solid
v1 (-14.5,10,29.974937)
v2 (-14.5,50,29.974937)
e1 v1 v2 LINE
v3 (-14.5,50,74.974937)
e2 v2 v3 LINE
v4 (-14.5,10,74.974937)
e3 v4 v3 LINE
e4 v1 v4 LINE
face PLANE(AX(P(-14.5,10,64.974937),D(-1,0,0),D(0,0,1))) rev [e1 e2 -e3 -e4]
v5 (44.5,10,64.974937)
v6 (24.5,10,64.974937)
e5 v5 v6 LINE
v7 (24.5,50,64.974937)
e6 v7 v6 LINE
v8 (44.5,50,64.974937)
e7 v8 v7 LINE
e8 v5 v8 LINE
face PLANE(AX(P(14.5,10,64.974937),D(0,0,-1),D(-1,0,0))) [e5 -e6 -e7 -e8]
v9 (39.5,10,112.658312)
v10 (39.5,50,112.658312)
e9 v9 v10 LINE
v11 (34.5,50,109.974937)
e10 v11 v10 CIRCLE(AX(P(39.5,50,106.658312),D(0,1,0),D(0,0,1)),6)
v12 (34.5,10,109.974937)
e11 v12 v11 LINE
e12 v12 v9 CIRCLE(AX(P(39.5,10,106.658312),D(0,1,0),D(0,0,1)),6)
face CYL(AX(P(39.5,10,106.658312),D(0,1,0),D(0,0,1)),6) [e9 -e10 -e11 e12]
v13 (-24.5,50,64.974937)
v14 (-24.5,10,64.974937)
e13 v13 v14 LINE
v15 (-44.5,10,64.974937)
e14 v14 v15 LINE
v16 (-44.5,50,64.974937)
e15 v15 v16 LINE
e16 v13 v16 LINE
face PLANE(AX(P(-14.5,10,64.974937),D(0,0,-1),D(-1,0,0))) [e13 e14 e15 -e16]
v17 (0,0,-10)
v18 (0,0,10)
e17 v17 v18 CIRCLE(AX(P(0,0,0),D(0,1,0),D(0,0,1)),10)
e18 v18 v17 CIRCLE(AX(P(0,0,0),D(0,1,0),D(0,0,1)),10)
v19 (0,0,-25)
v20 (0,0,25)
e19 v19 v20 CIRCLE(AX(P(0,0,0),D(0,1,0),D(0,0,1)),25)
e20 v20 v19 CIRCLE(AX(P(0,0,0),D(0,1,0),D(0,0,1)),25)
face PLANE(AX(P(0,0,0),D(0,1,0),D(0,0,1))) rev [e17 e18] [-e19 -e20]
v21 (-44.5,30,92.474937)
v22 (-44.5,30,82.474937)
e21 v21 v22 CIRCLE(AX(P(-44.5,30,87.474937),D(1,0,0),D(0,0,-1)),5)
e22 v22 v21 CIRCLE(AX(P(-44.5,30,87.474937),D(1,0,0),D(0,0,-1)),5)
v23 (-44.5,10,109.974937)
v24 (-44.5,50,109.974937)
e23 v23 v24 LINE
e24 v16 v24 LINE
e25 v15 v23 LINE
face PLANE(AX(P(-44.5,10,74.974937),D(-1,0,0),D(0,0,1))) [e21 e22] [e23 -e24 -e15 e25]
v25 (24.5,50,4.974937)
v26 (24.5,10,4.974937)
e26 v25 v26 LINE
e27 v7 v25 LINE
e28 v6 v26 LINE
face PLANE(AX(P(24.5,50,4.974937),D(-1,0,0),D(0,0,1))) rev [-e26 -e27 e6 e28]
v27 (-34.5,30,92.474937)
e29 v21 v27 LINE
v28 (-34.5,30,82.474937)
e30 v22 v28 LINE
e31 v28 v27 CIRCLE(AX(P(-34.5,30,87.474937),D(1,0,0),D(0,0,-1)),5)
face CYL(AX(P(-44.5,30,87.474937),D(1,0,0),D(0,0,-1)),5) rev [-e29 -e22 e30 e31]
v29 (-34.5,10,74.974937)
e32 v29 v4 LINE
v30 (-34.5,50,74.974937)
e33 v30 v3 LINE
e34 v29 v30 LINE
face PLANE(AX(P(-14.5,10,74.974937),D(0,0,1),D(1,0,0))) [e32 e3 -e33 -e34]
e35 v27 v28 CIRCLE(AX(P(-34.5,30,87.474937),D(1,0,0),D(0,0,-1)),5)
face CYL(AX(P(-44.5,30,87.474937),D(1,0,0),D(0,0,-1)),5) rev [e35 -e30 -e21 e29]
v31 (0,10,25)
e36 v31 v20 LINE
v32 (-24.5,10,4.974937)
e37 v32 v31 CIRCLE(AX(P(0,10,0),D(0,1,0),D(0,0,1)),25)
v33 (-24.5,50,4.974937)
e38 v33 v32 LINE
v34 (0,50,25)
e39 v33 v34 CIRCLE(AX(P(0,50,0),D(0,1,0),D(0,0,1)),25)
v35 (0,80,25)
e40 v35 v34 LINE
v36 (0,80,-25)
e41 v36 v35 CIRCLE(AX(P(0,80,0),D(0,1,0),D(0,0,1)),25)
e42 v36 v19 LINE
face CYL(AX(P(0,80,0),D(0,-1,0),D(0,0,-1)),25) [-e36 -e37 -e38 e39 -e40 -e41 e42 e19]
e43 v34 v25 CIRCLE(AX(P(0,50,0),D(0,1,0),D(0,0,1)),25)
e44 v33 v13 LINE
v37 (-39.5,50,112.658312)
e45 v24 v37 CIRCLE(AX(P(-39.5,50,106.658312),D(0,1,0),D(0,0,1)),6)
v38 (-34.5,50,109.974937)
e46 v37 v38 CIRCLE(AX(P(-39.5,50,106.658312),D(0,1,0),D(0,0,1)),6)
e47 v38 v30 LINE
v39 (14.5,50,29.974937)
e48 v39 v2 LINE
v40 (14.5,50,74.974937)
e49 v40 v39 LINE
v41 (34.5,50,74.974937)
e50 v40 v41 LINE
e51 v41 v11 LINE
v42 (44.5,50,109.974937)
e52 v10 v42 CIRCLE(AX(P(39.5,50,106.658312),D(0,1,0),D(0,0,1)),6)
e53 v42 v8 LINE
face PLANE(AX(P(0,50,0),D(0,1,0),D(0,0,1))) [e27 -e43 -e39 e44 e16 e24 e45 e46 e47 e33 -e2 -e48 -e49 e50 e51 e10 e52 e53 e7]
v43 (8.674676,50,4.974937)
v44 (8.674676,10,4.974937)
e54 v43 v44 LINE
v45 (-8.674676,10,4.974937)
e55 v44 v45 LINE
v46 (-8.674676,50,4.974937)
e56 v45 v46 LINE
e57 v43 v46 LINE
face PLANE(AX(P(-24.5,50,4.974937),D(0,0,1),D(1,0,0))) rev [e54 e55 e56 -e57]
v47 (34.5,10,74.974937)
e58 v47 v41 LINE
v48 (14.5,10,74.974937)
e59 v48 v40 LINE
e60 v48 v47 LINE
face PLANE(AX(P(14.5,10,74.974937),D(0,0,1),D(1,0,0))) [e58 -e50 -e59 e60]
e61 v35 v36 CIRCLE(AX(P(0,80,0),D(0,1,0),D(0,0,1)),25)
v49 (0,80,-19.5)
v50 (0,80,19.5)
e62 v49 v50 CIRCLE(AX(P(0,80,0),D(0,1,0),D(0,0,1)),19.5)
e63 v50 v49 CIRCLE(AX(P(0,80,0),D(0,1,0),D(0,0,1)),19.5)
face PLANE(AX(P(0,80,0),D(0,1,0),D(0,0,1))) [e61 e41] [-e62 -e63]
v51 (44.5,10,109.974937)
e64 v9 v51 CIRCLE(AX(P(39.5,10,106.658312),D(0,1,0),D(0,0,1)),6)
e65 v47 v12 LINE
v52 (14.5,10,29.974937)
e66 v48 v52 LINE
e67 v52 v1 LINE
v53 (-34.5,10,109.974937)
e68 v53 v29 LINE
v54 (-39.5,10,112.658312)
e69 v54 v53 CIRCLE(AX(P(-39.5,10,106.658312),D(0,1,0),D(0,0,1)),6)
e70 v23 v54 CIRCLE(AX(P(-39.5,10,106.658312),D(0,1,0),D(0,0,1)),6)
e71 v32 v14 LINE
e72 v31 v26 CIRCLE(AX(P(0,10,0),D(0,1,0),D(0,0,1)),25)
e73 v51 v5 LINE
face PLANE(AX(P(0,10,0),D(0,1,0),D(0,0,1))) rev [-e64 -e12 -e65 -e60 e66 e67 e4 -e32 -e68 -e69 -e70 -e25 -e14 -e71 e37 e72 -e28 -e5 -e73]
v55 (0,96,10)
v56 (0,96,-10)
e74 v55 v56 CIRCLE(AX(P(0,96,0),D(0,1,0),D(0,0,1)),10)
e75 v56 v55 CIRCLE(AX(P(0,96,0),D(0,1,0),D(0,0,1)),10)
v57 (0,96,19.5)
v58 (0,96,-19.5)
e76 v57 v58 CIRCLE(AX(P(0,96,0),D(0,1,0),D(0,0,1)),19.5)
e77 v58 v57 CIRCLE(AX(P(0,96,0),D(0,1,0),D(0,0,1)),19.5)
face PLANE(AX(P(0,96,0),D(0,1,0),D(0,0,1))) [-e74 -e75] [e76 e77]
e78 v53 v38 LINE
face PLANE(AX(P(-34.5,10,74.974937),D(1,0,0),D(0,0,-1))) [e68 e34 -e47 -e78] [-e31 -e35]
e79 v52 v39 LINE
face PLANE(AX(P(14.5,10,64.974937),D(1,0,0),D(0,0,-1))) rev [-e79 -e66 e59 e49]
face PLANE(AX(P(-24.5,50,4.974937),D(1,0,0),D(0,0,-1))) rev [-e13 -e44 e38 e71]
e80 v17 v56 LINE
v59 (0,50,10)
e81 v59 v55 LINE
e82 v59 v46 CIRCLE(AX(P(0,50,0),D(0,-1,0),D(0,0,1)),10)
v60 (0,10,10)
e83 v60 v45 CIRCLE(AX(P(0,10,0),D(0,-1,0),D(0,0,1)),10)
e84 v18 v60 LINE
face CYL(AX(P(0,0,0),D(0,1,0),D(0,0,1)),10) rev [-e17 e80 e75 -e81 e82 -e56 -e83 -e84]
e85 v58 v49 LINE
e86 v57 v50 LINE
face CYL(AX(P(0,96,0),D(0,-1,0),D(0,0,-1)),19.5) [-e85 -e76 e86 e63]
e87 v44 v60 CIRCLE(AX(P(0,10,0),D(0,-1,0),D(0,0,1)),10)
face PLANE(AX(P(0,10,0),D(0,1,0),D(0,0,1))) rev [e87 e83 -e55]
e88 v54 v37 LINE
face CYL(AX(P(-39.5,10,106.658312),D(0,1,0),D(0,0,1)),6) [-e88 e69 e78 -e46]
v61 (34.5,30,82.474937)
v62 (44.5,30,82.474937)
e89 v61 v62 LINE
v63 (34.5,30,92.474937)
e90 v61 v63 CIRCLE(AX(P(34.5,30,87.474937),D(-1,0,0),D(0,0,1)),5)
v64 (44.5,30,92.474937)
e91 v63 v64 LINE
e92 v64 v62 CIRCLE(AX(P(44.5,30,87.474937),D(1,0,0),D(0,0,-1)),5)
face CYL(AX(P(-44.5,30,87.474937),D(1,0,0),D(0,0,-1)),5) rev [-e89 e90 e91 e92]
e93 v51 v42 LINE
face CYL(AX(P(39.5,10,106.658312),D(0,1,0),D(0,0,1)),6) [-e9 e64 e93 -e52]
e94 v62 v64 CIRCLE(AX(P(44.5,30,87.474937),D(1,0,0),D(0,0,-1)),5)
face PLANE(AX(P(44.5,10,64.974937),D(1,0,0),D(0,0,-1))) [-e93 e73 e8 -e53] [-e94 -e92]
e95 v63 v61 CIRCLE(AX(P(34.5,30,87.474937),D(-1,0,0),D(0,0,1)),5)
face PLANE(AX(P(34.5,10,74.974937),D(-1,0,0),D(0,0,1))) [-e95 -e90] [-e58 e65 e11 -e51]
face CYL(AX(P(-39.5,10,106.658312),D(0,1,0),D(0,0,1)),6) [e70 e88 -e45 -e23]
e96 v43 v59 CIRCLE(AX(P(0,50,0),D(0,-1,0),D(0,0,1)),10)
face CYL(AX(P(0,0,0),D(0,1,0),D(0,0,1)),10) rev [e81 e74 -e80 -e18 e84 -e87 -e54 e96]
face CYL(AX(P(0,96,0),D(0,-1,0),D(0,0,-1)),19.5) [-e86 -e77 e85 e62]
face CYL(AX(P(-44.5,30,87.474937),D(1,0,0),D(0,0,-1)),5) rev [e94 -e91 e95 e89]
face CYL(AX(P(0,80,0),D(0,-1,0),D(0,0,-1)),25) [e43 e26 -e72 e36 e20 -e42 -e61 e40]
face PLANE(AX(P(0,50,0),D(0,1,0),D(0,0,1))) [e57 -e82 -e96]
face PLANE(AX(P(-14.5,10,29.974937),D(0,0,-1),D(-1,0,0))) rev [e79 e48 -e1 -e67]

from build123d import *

# Parameters (mm, degrees)
MAIN_BOSS_SKETCH_50_R  = 25
MAIN_BOSS_50X80_DEPTH  = 80
TOP_STEP_SKETCH_39_R   = 19.5
TOP_STEP_39X16_DEPTH   = 16
BORE_SKETCH_20_R       = 10
BORE_20_DEPTH          = 103.303470127
BRACKET_BLOCK_SKETCH_W = 49
BRACKET_BLOCK_SKETCH_H = 60
BRACKET_BLOCK_DEPTH    = 40
BRACKET_SLOT_SKETCH_W  = 29
BRACKET_SLOT_SKETCH_H  = 35
BRACKET_SLOT_DEPTH     = 40
MOUNTING_LUGS_DEPTH    = 40
LUG_HOLE_SKETCH_10_R   = 5
LUG_HOLES_10_DEPTH     = 173.710437877


with BuildPart() as part:
    # Main Boss Sketch Ø50 → Main Boss Ø50x80 (new body)
    with BuildSketch(Plane(origin=(0, 0, 0), x_dir=(1, 0, 0), z_dir=(0, 1, 0))):
        with Locations(Location((0, 0, 0), (0, 0, 270))):
            Circle(MAIN_BOSS_SKETCH_50_R)
    extrude(amount=MAIN_BOSS_50X80_DEPTH)

    # Top Step Sketch Ø39 → Top Step Ø39x16 (add)
    with BuildSketch(Plane(origin=(0, 80, 0), x_dir=(1, 0, 0), z_dir=(0, 1, 0))):
        with Locations(Location((0, 0, 0), (0, 0, 270))):
            Circle(TOP_STEP_SKETCH_39_R)
    extrude(amount=TOP_STEP_39X16_DEPTH)

    # Bore Sketch Ø20 → Bore Ø20 (cut, through all)
    with BuildSketch(Plane(origin=(0, 96, 0), x_dir=(1, 0, 0), z_dir=(0, 1, 0))):
        with Locations(Location((0, 0, 0), (0, 0, 270))):
            Circle(BORE_SKETCH_20_R)
    extrude(amount=-BORE_20_DEPTH, mode=Mode.SUBTRACT)

    # Bracket Block Sketch → Bracket Block (add)
    with BuildSketch(Plane(origin=(0, 10, 0), x_dir=(1, 0, 0), z_dir=(0, 1, 0))):
        with Locations((0, -34.974937186)):
            Rectangle(BRACKET_BLOCK_SKETCH_W, BRACKET_BLOCK_SKETCH_H)
    extrude(amount=BRACKET_BLOCK_DEPTH)

    # Bracket Slot Sketch → Bracket Slot (cut)
    with BuildSketch(Plane(origin=(0, 50, 0), x_dir=(1, 0, 0), z_dir=(0, 1, 0))):
        with Locations((0, -47.474937186)):
            Rectangle(BRACKET_SLOT_SKETCH_W, BRACKET_SLOT_SKETCH_H)
    extrude(amount=-BRACKET_SLOT_DEPTH, mode=Mode.SUBTRACT)

    # Mounting Lugs Sketch → Mounting Lugs (add)
    with BuildSketch(Plane(origin=(0, 50, 0), x_dir=(1, 0, 0), z_dir=(0, 1, 0))):
        with BuildLine():
            Line((14.5, -64.974937186), (44.5, -64.974937186))
            Line((44.5, -64.974937186), (44.5, -74.974937186))
            Line((44.5, -74.974937186), (44.5, -109.974937186))
            ThreePointArc((44.5, -109.974937186), (39.5, -112.658312395), (34.5, -109.974937186))
            Line((34.5, -109.974937186), (34.5, -74.974937186))
            Line((34.5, -74.974937186), (14.5, -74.974937186))
            Line((14.5, -74.974937186), (14.5, -64.974937186))
        make_face()
        with BuildLine():
            Line((-14.5, -64.974937186), (-44.5, -64.974937186))
            Line((-44.5, -64.974937186), (-44.5, -74.974937186))
            Line((-44.5, -74.974937186), (-44.5, -109.974937186))
            ThreePointArc((-44.5, -109.974937186), (-39.5, -112.658312395), (-34.5, -109.974937186))
            Line((-34.5, -109.974937186), (-34.5, -74.974937186))
            Line((-34.5, -74.974937186), (-14.5, -74.974937186))
            Line((-14.5, -74.974937186), (-14.5, -64.974937186))
        make_face()
    extrude(amount=-MOUNTING_LUGS_DEPTH)

    # Lug Hole Sketch Ø10 → Lug Holes Ø10 (cut, through all)
    with BuildSketch(Plane(origin=(44.5, 0, 0), x_dir=(0, 0, -1), z_dir=(1, 0, 0))):
        with Locations((-87.474937186, 30)):
            Circle(LUG_HOLE_SKETCH_10_R)
    extrude(amount=-LUG_HOLES_10_DEPTH, mode=Mode.SUBTRACT)


solid = part.part
